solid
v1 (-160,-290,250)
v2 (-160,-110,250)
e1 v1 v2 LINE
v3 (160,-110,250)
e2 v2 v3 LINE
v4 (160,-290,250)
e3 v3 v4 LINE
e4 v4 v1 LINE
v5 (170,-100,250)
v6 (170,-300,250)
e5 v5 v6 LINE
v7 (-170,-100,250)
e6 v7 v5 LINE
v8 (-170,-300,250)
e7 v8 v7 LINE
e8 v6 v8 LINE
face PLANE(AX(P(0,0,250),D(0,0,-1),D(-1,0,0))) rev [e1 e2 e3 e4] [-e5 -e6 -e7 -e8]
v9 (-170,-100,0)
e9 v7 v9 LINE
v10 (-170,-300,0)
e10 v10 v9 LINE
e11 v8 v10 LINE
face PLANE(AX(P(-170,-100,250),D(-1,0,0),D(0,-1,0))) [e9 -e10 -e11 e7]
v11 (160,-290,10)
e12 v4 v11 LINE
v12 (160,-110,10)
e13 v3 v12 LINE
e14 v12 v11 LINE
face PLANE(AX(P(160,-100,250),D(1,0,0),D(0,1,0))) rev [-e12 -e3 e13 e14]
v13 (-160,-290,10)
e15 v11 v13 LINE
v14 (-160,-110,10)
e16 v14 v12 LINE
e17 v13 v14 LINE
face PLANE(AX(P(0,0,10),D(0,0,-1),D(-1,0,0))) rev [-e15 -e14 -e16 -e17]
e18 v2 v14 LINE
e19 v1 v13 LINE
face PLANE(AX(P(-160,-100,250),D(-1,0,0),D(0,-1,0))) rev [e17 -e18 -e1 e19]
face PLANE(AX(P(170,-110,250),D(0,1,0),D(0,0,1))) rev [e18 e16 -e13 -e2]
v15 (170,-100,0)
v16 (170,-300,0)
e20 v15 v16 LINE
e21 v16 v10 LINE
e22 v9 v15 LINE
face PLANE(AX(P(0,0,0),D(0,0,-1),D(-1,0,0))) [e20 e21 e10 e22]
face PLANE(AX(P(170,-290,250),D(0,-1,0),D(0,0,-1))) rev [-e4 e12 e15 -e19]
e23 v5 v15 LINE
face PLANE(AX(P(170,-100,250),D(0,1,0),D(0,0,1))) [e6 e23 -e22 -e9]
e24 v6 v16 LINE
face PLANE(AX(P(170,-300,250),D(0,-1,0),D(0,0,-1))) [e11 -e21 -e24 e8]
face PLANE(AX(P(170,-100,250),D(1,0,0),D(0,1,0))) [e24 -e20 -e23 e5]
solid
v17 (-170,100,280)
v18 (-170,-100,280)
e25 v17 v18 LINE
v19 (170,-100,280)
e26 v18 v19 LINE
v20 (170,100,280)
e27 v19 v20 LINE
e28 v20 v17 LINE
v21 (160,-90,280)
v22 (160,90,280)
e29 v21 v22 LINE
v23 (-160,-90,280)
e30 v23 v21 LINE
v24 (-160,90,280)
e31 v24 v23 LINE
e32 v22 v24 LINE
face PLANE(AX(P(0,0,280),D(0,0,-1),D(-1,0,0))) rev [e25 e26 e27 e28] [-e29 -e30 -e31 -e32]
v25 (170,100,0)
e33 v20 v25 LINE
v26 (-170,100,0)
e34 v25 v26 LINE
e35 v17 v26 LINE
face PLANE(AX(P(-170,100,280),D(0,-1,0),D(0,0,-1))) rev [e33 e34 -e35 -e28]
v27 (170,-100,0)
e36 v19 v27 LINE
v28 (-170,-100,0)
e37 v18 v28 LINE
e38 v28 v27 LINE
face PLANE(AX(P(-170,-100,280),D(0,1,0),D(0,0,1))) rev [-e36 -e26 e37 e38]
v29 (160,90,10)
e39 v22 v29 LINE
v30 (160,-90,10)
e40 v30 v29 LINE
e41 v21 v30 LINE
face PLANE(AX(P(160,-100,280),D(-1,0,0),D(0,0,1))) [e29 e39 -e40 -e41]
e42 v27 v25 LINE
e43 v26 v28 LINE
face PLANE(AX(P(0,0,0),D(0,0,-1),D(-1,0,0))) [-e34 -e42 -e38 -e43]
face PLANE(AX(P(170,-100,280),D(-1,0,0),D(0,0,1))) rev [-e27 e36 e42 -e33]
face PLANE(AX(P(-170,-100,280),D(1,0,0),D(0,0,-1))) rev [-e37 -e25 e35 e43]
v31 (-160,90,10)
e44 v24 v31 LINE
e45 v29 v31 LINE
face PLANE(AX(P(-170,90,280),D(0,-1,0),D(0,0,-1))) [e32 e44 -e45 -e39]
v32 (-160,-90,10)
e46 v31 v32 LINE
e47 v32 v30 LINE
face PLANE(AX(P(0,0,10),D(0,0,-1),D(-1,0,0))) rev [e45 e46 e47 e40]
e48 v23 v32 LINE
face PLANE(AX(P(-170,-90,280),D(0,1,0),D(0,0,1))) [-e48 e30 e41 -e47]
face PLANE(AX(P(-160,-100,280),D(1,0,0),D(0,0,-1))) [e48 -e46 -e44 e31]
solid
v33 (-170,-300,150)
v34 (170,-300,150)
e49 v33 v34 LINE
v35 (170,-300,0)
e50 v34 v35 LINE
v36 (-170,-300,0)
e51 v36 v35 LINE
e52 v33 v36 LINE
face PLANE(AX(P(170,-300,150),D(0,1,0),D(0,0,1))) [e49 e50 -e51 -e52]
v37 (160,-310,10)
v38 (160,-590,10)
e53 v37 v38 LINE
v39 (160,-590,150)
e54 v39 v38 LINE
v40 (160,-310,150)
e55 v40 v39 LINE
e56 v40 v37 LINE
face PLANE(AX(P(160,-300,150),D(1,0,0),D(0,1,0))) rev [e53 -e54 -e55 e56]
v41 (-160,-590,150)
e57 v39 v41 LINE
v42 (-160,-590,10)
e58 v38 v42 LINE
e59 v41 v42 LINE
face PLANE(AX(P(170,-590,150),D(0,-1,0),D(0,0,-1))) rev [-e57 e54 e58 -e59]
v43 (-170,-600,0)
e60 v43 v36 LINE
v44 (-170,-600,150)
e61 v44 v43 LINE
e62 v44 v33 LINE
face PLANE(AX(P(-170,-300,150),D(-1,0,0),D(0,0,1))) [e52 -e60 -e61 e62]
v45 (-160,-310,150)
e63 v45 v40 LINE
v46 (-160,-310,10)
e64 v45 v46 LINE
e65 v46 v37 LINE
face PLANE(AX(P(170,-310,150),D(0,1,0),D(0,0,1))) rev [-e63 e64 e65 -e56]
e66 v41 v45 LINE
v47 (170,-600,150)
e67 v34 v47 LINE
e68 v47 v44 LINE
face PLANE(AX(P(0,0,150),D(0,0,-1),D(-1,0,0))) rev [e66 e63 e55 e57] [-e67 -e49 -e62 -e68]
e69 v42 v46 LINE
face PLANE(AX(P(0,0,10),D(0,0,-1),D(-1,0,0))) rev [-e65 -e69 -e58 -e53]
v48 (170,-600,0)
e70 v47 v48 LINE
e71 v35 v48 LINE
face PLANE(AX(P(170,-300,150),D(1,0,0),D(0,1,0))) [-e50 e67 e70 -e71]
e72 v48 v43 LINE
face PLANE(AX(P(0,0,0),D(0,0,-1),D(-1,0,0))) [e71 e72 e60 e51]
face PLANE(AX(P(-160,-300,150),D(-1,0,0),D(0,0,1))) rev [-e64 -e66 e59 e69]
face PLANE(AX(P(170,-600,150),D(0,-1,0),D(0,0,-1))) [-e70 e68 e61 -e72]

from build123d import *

# Parameters (mm, degrees)
SKETCH_1_W      = 340
SKETCH_1_H      = 200
EXTRUDE_1_DEPTH = 280
SHELL_1_T       = -10
SKETCH_2_W      = 340
SKETCH_2_H      = 200
EXTRUDE_2_DEPTH = 250
SHELL_2_T       = -10
SKETCH_3_W      = 340
SKETCH_3_H      = 300
EXTRUDE_3_DEPTH = 150
SHELL_3_T       = -10


with BuildPart() as part:
    # 草图1 → 凸台-拉伸1 (new body)
    with BuildSketch(Plane.XY):
        Rectangle(SKETCH_1_W, SKETCH_1_H)
    extrude(amount=EXTRUDE_1_DEPTH)

    # 抽壳1
    shell_1_openings = [part.faces().sort_by_distance(p)[0] for p in [
        (0, 0, 280),
    ]]
    offset(amount=SHELL_1_T, openings=shell_1_openings, kind=Kind.INTERSECTION)


with BuildPart() as body_2:
    # 草图2 → 凸台-拉伸2 (new body)
    with BuildSketch(Plane(origin=(0, 0, 0), x_dir=(-1, 0, 0), z_dir=(0, 0, -1))):
        with Locations((0, -200)):
            Rectangle(SKETCH_2_W, SKETCH_2_H)
    extrude(amount=-EXTRUDE_2_DEPTH)

    # 抽壳2
    shell_2_openings = [body_2.faces().sort_by_distance(p)[0] for p in [
        (0, -200, 250),
    ]]
    offset(amount=SHELL_2_T, openings=shell_2_openings, kind=Kind.INTERSECTION)


with BuildPart() as body_3:
    # 草图3 → 凸台-拉伸3 (new body)
    with BuildSketch(Plane(origin=(0, 0, 0), x_dir=(-1, 0, 0), z_dir=(0, 0, -1))):
        with Locations((0, -450)):
            Rectangle(SKETCH_3_W, SKETCH_3_H)
    extrude(amount=-EXTRUDE_3_DEPTH)

    # 抽壳3
    shell_3_openings = [body_3.faces().sort_by_distance(p)[0] for p in [
        (0, -450, 150),
    ]]
    offset(amount=SHELL_3_T, openings=shell_3_openings, kind=Kind.INTERSECTION)


solid = Compound([part.part, body_2.part, body_3.part])
